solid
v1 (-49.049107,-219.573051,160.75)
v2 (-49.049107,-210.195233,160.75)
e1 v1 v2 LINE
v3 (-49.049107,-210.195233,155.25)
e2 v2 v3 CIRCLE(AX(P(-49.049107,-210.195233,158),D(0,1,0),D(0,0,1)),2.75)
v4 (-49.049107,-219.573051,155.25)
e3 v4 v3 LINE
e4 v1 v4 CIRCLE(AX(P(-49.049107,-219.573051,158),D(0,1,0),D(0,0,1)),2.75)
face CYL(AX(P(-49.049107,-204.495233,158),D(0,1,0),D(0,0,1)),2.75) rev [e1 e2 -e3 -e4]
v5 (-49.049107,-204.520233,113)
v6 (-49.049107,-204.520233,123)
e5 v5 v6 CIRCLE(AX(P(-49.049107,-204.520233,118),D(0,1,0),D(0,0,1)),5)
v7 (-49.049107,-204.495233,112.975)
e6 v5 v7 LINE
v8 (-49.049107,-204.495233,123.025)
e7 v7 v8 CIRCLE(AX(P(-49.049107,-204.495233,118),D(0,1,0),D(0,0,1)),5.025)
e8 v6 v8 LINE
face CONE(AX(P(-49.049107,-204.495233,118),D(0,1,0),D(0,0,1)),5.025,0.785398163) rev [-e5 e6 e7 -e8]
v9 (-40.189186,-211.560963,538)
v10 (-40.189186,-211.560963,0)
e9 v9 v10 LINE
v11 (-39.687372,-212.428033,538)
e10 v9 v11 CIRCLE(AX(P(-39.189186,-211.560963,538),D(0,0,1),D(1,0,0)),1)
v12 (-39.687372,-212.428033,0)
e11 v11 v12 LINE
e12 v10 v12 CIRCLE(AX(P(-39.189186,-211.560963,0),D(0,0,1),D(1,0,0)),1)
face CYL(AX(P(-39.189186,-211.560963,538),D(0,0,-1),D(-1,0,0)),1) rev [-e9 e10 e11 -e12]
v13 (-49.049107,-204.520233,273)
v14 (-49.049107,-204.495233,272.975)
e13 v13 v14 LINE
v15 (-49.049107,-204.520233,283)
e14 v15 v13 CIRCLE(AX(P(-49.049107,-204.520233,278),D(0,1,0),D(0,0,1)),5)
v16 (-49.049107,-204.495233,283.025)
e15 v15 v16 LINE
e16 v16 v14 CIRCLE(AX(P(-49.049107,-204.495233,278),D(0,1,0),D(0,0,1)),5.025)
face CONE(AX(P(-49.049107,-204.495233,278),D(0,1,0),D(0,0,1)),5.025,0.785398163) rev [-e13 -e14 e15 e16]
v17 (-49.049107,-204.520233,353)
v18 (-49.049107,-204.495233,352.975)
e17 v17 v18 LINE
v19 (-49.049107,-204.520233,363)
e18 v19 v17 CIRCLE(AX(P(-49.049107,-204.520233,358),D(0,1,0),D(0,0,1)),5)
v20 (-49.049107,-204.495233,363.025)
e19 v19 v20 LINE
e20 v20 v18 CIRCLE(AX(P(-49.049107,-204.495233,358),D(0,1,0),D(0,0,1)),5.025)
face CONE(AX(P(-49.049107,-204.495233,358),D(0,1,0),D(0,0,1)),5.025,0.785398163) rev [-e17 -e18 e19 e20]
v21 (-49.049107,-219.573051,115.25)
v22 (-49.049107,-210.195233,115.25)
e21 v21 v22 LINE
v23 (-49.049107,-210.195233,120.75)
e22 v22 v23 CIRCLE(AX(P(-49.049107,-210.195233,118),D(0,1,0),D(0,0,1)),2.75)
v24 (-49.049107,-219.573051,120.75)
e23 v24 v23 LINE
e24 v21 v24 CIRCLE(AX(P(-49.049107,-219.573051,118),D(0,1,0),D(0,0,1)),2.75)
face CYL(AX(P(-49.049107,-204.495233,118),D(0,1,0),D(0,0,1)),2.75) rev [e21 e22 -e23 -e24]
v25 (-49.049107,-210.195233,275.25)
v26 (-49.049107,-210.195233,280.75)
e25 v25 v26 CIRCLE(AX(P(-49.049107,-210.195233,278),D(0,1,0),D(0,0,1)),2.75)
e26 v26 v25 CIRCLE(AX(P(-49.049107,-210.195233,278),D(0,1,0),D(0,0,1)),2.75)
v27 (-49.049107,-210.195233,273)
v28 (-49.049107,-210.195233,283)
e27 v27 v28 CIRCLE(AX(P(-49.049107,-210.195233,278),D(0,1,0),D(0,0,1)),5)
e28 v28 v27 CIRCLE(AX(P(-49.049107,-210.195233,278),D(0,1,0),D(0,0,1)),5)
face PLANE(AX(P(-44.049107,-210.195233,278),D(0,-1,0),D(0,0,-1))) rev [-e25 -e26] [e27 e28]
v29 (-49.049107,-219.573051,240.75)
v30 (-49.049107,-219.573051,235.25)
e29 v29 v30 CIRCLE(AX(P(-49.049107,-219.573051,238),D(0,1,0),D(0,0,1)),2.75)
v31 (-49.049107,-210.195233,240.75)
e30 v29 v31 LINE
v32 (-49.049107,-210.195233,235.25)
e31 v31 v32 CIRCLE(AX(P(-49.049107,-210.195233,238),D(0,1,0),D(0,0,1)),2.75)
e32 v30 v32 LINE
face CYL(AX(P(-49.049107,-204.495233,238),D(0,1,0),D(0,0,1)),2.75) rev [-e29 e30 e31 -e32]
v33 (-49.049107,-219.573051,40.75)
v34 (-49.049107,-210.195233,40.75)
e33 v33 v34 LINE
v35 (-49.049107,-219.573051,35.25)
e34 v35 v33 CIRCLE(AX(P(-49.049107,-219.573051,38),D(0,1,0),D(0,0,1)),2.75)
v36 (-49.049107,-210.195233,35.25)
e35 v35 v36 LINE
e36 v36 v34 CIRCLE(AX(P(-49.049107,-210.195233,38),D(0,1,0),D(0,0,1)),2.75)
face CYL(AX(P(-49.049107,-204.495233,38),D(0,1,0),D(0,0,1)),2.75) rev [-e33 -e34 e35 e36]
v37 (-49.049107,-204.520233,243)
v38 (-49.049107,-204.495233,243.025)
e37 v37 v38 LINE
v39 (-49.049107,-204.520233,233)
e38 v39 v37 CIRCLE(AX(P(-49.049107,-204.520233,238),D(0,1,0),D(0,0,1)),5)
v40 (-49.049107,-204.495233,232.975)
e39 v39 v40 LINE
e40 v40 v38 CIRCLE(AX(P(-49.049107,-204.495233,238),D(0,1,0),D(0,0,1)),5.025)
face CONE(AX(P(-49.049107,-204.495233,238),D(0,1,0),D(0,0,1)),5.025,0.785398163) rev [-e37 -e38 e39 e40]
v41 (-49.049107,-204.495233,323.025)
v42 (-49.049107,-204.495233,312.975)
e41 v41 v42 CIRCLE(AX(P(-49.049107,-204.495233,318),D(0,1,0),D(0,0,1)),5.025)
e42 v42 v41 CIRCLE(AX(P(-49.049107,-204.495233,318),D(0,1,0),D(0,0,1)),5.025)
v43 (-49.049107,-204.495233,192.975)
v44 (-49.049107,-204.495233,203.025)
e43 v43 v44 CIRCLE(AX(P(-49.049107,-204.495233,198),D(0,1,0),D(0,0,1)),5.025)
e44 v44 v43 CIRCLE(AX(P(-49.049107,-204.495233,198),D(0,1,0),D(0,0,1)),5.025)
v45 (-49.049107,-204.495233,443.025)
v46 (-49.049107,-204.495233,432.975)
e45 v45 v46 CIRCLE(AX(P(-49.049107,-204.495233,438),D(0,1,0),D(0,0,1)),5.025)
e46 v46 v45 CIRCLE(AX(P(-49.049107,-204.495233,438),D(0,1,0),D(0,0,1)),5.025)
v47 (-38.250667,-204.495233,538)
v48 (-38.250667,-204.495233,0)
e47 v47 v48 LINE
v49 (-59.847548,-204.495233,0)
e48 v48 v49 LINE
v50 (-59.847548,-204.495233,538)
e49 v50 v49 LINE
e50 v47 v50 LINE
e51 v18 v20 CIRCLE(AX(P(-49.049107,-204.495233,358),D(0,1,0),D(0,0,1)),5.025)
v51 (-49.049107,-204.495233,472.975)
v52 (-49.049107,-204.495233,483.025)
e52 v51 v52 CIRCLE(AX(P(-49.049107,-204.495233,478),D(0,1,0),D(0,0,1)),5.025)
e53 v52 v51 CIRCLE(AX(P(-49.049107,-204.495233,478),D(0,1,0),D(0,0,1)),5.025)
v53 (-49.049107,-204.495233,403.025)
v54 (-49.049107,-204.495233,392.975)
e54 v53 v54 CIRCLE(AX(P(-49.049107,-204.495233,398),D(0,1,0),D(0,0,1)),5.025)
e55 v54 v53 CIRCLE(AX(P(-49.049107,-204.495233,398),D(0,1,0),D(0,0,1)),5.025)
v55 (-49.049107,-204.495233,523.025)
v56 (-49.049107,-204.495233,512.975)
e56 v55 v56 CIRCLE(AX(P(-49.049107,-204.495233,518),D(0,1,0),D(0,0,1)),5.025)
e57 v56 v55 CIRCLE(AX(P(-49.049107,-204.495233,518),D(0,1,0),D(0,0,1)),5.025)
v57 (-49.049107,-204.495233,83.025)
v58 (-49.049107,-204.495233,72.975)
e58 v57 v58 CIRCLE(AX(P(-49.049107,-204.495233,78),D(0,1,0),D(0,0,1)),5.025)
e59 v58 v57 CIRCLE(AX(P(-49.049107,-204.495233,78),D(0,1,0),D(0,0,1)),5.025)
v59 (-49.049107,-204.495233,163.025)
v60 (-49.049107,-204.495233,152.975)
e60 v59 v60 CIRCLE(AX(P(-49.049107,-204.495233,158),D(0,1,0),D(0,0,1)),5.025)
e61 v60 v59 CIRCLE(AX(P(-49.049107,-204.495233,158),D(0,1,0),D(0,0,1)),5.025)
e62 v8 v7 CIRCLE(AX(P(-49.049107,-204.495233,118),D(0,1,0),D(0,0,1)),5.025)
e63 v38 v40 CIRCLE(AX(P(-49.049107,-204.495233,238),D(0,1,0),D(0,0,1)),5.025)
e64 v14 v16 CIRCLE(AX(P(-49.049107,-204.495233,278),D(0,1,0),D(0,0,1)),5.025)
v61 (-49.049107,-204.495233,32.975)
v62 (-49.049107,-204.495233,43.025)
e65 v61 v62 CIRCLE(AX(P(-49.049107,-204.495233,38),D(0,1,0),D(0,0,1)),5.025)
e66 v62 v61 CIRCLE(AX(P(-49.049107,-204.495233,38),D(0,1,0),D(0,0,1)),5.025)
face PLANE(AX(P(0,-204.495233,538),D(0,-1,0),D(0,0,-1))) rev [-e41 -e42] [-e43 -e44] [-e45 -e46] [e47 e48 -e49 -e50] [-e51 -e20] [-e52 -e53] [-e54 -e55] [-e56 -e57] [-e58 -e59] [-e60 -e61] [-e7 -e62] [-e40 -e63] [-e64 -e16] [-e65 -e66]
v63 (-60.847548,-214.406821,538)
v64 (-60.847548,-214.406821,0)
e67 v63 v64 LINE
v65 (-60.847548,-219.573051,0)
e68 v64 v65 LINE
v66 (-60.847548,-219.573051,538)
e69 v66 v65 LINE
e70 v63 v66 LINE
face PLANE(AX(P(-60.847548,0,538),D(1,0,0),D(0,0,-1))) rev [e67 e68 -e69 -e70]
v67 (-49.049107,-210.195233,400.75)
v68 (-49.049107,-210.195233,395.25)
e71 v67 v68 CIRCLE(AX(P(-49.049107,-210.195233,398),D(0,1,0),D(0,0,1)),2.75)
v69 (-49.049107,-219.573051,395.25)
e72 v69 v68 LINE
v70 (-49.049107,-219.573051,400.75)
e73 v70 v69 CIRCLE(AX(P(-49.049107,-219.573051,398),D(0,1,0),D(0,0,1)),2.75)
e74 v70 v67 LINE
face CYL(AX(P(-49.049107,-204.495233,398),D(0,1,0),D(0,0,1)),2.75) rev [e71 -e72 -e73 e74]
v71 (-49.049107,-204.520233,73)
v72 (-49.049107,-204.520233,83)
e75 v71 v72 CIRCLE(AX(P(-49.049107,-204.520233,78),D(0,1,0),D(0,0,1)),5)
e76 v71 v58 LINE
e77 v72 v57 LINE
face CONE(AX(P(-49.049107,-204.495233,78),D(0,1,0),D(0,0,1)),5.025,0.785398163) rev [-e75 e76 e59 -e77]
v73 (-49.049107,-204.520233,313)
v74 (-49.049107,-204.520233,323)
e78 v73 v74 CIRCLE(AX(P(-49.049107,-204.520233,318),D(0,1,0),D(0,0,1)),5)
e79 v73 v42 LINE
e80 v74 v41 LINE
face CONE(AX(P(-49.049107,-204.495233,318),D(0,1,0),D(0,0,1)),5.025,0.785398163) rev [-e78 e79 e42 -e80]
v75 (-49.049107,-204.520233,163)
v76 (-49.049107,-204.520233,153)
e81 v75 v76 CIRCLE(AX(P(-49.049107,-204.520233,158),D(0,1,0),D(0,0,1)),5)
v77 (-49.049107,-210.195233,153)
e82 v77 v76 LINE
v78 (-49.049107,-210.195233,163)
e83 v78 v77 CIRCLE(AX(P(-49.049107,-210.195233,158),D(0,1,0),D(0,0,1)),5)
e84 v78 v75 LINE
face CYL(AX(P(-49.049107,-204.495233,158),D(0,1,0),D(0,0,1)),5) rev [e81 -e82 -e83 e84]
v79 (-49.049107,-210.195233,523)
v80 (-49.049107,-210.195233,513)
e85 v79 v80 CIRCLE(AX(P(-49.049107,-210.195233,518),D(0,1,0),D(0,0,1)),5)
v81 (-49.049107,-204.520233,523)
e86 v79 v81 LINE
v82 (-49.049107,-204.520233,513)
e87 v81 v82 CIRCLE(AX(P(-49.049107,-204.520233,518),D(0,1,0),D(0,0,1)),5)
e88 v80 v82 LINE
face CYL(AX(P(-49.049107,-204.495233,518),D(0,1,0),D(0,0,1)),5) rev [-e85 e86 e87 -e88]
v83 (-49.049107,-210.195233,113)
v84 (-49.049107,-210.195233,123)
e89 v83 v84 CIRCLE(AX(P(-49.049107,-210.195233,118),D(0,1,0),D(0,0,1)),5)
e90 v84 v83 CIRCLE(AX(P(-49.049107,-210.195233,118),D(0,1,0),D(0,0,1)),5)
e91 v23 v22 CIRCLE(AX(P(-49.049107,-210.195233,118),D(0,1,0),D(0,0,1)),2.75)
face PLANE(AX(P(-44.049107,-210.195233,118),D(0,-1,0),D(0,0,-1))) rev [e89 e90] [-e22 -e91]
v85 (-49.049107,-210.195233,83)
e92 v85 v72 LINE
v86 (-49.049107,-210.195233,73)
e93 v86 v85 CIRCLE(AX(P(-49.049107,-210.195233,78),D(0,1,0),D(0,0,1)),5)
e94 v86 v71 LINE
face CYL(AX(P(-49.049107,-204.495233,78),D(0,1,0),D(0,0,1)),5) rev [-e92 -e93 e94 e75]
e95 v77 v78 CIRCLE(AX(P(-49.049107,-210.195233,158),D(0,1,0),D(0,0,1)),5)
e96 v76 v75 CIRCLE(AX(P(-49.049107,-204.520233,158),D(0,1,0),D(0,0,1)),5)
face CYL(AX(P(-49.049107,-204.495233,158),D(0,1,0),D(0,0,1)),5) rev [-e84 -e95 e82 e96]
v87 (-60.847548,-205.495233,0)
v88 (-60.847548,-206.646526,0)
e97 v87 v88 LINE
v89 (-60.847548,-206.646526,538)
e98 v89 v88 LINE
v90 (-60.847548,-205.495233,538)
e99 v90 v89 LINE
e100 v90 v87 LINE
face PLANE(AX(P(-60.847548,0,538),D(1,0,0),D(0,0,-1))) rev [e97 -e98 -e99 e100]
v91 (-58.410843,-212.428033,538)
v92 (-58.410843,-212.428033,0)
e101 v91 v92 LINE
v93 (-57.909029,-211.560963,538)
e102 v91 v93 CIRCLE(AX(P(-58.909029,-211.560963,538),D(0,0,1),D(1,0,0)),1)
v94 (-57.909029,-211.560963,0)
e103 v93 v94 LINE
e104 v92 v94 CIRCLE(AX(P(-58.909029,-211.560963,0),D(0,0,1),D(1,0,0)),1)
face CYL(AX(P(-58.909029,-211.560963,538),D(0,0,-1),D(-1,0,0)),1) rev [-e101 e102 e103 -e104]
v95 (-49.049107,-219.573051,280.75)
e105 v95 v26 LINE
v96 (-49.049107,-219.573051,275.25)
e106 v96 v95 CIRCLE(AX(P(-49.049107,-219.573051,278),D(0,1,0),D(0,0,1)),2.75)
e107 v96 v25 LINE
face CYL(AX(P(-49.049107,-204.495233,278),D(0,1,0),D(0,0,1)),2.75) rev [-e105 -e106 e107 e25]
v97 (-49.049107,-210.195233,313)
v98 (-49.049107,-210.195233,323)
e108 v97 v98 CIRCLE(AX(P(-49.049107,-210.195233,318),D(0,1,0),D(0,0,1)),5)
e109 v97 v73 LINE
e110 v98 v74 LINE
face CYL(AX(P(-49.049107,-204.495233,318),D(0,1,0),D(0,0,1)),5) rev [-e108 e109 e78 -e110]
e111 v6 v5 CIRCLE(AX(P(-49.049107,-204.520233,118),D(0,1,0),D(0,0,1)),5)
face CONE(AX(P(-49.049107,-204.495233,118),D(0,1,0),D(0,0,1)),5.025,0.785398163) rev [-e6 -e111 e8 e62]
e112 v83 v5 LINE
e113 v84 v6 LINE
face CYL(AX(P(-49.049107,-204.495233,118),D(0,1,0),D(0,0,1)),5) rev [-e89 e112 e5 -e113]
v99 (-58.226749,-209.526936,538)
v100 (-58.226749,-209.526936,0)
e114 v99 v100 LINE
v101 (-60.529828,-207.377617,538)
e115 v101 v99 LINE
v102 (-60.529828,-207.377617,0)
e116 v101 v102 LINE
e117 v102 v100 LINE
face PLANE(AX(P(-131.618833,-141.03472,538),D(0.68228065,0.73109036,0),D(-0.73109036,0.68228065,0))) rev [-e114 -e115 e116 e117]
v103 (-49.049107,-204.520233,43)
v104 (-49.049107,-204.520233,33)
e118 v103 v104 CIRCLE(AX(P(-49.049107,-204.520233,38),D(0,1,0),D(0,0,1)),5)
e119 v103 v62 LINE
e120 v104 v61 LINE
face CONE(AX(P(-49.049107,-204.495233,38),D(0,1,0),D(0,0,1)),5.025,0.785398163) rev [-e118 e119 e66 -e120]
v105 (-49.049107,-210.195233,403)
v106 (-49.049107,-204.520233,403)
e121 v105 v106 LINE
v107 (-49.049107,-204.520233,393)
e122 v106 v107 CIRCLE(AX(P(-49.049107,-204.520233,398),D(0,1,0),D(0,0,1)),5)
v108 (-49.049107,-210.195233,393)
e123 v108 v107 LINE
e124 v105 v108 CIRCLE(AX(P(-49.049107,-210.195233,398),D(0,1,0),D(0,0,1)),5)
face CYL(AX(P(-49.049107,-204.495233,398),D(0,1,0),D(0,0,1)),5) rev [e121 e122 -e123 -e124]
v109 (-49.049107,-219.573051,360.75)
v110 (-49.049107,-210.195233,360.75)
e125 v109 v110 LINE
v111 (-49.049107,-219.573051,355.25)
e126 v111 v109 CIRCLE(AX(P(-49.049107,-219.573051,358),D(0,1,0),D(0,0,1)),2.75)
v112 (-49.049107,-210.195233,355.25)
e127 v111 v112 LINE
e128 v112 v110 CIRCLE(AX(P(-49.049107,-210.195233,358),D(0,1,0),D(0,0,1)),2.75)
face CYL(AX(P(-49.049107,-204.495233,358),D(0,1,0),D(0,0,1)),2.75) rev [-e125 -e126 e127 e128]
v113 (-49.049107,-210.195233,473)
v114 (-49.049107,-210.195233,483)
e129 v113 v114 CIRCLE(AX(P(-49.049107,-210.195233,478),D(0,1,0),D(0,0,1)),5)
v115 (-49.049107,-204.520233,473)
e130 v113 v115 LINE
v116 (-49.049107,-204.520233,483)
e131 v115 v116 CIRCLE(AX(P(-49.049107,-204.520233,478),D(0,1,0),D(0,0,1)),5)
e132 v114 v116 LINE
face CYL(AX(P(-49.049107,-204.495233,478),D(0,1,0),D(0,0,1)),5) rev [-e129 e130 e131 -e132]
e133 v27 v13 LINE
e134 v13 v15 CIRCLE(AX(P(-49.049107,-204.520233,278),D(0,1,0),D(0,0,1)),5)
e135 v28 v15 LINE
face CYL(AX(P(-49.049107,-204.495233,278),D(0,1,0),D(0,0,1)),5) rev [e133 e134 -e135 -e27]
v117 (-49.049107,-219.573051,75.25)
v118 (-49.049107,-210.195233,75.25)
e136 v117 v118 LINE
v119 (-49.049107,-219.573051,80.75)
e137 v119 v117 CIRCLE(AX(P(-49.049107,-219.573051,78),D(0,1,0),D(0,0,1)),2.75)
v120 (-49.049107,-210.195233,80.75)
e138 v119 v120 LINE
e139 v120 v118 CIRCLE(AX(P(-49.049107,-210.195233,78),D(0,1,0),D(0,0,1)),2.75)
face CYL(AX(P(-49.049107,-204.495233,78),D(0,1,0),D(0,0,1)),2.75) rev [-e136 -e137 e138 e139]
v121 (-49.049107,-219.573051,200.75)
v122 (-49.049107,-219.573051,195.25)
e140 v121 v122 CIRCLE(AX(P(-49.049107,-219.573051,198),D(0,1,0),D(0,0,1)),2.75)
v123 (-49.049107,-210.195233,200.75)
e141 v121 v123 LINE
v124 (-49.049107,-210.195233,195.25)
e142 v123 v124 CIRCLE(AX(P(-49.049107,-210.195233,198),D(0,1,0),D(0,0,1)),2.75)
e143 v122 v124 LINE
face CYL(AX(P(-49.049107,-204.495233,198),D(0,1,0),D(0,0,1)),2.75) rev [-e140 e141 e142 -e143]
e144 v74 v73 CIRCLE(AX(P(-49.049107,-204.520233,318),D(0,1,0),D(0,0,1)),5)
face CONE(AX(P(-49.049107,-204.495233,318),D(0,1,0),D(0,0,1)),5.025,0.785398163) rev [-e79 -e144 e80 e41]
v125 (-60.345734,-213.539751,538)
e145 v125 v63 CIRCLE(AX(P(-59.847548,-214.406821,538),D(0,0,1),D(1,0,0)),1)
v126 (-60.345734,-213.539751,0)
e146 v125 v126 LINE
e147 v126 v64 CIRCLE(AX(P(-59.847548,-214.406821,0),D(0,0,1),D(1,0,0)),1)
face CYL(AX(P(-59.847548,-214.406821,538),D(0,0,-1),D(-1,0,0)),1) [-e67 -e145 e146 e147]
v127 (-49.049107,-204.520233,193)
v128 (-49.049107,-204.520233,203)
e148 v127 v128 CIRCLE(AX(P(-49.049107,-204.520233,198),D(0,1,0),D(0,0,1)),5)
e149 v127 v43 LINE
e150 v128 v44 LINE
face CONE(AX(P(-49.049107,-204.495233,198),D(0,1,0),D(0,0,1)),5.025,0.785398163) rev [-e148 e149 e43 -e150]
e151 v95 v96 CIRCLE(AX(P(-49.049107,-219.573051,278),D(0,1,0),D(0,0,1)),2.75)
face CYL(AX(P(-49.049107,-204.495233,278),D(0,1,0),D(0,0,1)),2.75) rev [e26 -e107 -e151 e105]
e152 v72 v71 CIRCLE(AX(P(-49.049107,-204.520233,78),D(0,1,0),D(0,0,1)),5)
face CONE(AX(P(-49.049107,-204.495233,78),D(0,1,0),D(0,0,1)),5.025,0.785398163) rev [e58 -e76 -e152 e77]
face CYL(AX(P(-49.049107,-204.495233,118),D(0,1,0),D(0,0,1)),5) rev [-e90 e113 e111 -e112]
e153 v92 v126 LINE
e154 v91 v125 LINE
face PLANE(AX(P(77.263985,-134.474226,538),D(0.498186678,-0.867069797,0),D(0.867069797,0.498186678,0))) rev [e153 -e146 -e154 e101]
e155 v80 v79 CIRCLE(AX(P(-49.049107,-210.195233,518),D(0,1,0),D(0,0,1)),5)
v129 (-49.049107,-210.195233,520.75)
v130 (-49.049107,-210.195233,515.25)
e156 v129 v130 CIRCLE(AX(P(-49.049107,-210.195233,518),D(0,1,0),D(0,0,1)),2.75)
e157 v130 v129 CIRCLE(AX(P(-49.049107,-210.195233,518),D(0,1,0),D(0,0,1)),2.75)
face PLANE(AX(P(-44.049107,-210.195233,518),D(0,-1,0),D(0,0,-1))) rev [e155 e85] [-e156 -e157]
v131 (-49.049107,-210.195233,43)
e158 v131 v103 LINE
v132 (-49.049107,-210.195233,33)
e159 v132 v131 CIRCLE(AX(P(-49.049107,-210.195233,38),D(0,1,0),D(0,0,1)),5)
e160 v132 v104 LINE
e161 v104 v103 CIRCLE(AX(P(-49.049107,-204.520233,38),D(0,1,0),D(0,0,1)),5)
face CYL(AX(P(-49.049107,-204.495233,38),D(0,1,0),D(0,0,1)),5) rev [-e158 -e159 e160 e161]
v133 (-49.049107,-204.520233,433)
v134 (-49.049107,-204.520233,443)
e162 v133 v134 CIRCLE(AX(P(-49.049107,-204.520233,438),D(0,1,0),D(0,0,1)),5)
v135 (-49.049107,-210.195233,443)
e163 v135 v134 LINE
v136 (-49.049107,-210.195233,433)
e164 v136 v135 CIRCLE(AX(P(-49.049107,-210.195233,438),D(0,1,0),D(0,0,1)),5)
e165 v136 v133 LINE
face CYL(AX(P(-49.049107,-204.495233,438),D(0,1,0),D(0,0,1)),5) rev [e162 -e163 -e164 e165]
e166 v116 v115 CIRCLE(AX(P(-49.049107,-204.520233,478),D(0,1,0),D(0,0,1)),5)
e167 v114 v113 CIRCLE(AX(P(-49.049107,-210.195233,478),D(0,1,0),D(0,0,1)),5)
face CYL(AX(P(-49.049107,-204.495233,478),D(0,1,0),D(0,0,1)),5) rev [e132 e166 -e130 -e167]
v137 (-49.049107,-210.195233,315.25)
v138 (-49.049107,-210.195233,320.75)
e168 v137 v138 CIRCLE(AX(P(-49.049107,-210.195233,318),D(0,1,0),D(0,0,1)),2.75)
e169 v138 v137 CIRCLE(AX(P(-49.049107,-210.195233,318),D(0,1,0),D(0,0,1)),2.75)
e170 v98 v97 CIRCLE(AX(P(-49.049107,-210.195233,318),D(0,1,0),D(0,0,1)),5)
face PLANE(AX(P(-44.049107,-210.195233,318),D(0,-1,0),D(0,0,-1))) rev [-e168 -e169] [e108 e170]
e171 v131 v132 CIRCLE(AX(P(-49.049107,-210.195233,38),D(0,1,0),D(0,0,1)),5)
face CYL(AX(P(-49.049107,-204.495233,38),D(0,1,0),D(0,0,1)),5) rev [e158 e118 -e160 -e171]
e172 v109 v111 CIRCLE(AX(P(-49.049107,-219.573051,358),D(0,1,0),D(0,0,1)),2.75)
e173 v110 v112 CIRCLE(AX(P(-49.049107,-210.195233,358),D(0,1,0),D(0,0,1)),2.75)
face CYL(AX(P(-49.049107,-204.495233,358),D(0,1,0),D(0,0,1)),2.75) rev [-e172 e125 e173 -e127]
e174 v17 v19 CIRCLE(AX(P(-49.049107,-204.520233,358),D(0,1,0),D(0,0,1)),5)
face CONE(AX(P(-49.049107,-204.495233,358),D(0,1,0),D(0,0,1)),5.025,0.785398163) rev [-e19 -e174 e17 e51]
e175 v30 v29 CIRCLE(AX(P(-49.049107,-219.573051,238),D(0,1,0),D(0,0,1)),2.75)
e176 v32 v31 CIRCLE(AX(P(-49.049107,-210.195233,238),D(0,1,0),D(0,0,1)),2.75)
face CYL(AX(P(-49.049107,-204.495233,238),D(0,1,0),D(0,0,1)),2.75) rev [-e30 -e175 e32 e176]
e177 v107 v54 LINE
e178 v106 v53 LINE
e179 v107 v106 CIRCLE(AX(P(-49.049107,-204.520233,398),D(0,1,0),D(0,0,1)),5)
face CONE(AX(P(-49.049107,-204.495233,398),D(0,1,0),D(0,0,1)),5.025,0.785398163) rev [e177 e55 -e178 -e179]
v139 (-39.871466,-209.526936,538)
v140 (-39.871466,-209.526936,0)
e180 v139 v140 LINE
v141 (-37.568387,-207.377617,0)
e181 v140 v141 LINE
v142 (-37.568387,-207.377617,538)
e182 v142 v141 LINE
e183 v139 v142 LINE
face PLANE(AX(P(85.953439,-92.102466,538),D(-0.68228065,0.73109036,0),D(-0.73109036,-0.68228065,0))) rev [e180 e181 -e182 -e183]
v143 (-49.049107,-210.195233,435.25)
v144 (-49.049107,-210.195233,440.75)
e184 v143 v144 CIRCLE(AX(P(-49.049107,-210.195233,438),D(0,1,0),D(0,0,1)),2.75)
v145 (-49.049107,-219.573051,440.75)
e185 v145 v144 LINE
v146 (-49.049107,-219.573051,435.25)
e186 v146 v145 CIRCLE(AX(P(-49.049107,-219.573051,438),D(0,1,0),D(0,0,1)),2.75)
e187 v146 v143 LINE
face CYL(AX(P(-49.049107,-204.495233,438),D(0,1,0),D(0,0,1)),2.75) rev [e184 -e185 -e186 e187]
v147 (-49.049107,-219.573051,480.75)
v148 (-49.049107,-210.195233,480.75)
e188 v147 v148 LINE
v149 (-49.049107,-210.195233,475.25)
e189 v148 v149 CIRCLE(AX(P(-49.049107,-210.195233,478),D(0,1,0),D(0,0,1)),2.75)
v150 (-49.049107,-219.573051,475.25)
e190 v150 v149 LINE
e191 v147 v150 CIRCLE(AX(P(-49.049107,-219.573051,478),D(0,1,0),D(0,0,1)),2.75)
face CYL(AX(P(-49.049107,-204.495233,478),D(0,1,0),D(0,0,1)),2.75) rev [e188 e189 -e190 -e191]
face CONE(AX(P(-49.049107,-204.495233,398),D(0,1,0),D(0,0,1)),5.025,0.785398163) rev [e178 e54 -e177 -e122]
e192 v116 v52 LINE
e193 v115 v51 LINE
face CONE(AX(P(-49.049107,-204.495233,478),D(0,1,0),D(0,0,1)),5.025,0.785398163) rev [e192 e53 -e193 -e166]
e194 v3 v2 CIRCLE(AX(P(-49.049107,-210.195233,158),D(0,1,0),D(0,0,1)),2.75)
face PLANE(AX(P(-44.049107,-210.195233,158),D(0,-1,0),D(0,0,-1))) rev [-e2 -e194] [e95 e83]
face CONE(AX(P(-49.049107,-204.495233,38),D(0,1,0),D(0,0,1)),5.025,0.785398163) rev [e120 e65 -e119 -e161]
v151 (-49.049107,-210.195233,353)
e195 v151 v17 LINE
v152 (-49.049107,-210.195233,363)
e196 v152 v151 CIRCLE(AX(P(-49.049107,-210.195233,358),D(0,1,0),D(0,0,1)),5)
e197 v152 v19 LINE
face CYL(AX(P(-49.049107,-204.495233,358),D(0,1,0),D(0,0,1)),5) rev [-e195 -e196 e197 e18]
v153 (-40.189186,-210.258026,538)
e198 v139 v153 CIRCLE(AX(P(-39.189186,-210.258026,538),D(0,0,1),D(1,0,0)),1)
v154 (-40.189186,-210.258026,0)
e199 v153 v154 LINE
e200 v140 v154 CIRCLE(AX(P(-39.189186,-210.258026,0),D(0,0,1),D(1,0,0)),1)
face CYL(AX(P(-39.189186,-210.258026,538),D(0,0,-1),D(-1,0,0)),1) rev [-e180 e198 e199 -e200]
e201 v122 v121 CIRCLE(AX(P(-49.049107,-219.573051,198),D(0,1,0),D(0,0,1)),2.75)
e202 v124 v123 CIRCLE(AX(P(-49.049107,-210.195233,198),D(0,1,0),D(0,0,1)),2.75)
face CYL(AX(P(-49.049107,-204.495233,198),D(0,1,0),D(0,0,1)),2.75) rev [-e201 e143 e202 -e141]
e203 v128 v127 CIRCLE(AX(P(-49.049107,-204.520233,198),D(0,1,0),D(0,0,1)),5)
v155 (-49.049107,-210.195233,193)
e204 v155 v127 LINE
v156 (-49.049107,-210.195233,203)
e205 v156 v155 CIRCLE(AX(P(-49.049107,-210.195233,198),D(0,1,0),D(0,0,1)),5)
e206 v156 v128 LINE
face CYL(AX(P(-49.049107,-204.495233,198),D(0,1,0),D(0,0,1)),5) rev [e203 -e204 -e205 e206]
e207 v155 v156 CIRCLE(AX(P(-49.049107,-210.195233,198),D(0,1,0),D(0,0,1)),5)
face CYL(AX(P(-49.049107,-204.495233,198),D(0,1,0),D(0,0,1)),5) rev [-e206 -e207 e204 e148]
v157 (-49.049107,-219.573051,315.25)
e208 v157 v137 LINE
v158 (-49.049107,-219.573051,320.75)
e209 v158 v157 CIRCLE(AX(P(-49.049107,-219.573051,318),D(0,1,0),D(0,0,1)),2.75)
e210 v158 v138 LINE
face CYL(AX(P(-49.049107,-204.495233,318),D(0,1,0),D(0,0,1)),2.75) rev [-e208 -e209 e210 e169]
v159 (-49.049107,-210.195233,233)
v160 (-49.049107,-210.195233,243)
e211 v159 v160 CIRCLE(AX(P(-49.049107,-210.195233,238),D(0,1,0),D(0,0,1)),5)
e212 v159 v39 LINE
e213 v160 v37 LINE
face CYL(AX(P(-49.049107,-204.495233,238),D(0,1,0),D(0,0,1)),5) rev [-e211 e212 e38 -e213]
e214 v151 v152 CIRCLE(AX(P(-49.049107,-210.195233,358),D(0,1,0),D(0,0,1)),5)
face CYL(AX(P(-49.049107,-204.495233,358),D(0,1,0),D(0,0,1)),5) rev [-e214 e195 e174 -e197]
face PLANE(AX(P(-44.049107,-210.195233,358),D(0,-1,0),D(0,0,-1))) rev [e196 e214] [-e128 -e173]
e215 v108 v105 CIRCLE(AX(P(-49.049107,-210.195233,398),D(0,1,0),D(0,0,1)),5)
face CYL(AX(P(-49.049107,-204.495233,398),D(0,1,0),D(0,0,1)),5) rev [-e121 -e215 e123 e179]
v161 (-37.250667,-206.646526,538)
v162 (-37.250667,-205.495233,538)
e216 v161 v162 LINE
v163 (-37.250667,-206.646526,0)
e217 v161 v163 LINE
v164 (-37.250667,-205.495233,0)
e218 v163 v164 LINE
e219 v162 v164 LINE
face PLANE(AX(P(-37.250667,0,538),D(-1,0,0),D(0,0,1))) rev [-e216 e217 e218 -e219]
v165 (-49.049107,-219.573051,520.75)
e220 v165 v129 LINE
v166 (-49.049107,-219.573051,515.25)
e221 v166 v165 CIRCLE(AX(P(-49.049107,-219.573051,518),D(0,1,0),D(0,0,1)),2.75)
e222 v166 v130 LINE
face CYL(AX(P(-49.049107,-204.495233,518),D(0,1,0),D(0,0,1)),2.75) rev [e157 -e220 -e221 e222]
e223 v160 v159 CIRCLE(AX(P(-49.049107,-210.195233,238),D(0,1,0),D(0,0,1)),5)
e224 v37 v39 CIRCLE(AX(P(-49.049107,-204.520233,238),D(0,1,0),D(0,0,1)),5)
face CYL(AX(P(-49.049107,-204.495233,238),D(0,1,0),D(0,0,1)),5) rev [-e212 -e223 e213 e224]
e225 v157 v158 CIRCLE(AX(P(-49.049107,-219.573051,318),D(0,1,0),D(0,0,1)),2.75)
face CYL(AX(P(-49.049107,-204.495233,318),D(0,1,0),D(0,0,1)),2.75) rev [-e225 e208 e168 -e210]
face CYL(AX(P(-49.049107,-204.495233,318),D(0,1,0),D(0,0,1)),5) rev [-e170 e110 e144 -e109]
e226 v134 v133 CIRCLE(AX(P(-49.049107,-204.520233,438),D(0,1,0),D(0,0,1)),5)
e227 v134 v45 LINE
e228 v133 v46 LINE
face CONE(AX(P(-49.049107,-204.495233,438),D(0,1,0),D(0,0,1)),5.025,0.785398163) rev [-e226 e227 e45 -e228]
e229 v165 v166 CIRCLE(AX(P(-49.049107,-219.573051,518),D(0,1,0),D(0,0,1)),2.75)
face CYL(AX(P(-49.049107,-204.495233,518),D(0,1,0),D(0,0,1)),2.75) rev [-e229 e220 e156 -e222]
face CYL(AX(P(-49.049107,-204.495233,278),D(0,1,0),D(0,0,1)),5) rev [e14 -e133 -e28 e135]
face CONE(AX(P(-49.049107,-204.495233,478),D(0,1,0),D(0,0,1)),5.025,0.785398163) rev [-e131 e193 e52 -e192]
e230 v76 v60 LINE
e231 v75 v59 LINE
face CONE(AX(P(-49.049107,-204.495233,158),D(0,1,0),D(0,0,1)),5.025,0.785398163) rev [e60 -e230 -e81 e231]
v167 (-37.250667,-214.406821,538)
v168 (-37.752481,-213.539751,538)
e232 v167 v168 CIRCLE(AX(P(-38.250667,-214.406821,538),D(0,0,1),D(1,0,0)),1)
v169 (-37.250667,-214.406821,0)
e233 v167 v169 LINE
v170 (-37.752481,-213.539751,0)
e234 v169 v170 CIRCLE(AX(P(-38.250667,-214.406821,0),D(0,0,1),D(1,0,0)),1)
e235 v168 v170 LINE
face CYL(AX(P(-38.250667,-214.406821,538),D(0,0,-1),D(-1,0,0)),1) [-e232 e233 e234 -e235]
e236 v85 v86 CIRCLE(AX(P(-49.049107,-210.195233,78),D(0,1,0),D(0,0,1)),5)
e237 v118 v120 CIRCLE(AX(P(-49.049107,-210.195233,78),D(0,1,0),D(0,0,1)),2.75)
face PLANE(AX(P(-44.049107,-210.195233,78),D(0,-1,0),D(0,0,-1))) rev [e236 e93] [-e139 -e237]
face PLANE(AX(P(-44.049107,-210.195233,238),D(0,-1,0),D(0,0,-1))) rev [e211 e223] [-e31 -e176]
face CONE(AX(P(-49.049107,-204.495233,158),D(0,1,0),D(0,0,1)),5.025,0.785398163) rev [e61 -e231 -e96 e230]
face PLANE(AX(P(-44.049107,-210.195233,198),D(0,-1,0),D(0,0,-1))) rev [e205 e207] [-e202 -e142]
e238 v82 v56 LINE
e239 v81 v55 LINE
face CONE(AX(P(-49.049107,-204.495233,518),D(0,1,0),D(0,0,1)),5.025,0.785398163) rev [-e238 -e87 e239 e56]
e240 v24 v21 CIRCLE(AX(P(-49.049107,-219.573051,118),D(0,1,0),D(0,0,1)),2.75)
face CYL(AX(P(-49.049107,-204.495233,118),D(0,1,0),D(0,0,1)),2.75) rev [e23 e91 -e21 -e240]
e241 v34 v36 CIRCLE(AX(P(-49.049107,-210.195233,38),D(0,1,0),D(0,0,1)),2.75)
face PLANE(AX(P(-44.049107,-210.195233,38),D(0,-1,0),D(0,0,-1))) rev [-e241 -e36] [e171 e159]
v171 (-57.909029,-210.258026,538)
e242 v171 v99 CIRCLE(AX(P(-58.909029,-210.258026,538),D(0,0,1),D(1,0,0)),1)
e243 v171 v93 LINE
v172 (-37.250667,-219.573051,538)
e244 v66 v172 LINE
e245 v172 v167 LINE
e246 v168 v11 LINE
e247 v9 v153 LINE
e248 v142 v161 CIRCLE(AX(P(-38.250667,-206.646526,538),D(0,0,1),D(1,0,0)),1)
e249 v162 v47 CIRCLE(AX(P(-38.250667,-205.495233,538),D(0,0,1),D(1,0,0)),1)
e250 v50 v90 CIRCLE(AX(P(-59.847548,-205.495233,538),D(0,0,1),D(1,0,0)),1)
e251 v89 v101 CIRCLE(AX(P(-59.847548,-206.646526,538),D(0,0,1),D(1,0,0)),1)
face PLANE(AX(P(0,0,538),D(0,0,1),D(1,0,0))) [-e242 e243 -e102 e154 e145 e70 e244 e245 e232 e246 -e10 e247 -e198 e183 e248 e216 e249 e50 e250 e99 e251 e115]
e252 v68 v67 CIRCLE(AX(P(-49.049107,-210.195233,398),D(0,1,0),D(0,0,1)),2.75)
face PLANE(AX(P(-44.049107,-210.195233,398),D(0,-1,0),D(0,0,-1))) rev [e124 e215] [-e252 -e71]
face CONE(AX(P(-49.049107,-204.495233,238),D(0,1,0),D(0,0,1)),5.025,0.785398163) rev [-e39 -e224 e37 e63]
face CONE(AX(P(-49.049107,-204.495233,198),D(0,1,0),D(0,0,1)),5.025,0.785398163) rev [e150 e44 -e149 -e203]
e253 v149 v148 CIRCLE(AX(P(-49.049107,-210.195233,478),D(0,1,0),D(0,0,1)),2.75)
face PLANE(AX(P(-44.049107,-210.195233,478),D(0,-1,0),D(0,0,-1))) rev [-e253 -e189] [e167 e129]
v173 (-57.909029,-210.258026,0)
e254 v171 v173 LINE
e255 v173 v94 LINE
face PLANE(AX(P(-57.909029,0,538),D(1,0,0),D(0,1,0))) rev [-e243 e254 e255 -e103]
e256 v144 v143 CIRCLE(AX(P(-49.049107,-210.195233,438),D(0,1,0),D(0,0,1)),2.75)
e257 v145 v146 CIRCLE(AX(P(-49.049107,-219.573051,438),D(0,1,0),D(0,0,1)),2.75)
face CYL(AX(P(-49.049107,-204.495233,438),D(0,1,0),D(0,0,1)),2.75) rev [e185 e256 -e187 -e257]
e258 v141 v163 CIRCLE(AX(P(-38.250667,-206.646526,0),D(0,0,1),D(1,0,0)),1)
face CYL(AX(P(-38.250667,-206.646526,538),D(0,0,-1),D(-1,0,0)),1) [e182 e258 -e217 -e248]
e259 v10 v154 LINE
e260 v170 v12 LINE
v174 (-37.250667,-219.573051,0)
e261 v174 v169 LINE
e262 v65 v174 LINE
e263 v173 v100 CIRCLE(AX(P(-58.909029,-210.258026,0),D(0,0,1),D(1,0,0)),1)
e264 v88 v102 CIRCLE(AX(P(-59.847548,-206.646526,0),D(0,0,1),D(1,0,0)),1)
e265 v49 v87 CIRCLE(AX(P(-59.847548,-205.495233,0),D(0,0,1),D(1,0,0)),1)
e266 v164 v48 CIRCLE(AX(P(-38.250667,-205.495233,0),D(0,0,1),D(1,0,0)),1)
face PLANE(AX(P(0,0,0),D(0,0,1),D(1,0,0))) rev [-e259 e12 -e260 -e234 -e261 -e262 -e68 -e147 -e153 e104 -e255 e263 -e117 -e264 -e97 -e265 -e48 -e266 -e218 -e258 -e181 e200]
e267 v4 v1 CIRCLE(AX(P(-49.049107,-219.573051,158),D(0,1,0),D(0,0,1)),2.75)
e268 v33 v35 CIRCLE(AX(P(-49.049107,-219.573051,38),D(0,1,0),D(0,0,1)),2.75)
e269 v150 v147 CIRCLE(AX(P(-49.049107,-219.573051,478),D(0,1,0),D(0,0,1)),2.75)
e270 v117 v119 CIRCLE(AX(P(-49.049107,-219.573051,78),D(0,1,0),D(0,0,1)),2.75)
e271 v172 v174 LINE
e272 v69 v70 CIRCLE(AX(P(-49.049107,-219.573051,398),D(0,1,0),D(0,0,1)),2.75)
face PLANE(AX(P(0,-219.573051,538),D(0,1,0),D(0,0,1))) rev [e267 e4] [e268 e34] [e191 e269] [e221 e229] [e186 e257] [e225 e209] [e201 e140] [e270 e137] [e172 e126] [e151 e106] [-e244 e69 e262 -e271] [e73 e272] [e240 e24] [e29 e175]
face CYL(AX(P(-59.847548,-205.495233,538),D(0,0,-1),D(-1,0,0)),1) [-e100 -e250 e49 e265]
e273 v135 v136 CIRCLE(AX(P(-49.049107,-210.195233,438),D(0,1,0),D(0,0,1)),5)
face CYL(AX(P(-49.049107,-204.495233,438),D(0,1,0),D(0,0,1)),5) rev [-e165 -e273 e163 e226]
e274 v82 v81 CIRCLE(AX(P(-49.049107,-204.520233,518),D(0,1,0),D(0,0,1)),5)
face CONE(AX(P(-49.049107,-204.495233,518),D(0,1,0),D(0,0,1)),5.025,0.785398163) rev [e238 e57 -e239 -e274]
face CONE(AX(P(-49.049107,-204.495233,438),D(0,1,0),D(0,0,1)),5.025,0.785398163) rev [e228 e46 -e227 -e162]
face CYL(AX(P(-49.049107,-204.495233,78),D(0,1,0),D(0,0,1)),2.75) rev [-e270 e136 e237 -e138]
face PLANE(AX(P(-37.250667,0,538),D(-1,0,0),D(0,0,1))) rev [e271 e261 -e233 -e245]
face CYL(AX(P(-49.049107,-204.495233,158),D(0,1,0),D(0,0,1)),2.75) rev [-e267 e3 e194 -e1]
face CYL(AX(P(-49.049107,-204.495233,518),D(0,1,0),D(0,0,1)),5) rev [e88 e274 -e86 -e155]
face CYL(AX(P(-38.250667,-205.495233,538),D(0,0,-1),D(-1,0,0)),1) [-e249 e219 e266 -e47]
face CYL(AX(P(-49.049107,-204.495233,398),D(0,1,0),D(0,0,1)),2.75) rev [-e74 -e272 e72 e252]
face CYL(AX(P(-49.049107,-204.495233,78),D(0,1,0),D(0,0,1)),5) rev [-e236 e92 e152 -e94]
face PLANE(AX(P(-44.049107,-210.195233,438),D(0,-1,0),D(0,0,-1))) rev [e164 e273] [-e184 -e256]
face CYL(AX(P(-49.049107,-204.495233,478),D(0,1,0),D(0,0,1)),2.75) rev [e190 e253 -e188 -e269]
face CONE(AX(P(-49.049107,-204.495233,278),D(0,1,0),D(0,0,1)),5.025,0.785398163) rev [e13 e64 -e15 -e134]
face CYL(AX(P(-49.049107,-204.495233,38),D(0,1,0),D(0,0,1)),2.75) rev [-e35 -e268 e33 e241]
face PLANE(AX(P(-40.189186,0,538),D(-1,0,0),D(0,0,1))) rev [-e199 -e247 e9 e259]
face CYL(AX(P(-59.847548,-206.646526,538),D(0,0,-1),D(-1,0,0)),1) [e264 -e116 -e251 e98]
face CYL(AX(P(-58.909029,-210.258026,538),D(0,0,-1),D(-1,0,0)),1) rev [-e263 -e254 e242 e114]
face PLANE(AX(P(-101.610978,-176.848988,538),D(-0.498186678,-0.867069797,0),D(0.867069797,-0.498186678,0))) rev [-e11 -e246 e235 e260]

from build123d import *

# Parameters (mm, degrees)
BOSS_EXTRUDE1_DEPTH                           = 538
CBORE_FOR_M5_HEXAGON_SOCKET_HEAD_CAP_2_COUNT  = 2
CBORE_FOR_M5_HEXAGON_SOCKET_HEAD_CAP_2_PITCH  = 40
CBORE_FOR_M5_HEXAGON_SOCKET_HEAD_CAP_3_COUNT  = 2
CBORE_FOR_M5_HEXAGON_SOCKET_HEAD_CAP_3_PITCH  = 80
CBORE_FOR_M5_HEXAGON_SOCKET_HEAD_CAP_4_COUNT  = 2
CBORE_FOR_M5_HEXAGON_SOCKET_HEAD_CAP_4_PITCH  = 120
CBORE_FOR_M5_HEXAGON_SOCKET_HEAD_CAP_5_COUNT  = 2
CBORE_FOR_M5_HEXAGON_SOCKET_HEAD_CAP_5_PITCH  = 160
CBORE_FOR_M5_HEXAGON_SOCKET_HEAD_CAP_6_COUNT  = 2
CBORE_FOR_M5_HEXAGON_SOCKET_HEAD_CAP_6_PITCH  = 200
CBORE_FOR_M5_HEXAGON_SOCKET_HEAD_CAP_7_COUNT  = 2
CBORE_FOR_M5_HEXAGON_SOCKET_HEAD_CAP_7_PITCH  = 240
CBORE_FOR_M5_HEXAGON_SOCKET_HEAD_CAP_8_COUNT  = 2
CBORE_FOR_M5_HEXAGON_SOCKET_HEAD_CAP_8_PITCH  = 280
CBORE_FOR_M5_HEXAGON_SOCKET_HEAD_CAP_9_COUNT  = 2
CBORE_FOR_M5_HEXAGON_SOCKET_HEAD_CAP_9_PITCH  = 320
CBORE_FOR_M5_HEXAGON_SOCKET_HEAD_CAP_10_COUNT = 2
CBORE_FOR_M5_HEXAGON_SOCKET_HEAD_CAP_10_PITCH = 360
CBORE_FOR_M5_HEXAGON_SOCKET_HEAD_CAP_11_COUNT = 2
CBORE_FOR_M5_HEXAGON_SOCKET_HEAD_CAP_11_PITCH = 400
CBORE_FOR_M5_HEXAGON_SOCKET_HEAD_CAP_12_COUNT = 2
CBORE_FOR_M5_HEXAGON_SOCKET_HEAD_CAP_12_PITCH = 440
CBORE_FOR_M5_HEXAGON_SOCKET_HEAD_CAP_13_COUNT = 2
CBORE_FOR_M5_HEXAGON_SOCKET_HEAD_CAP_13_PITCH = 480


with BuildPart() as part:
    # Sketch1 → Boss-Extrude1 (new body)
    with BuildSketch(Plane.XY):
        with BuildLine():
            Line((-49.04910749, -219.573051322), (-49.04910749, -215.151654368))
            Line((-49.04910749, -215.151654368), (-49.04910749, -204.495232783))
            Line((-49.04910749, -204.495232783), (-59.847547756, -204.495232783))
            ThreePointArc((-59.847547756, -204.495232783), (-60.554654537, -204.788126002), (-60.847547756, -205.495232783))
            Line((-60.847547756, -205.495232783), (-60.847547756, -206.646526247))
            ThreePointArc((-60.847547756, -206.646526247), (-60.764684782, -207.045098292), (-60.529828406, -207.377616608))
            Line((-60.529828406, -207.377616608), (-58.226748647, -209.52693609))
            ThreePointArc((-58.226748647, -209.52693609), (-57.991892271, -209.859454405), (-57.909029297, -210.25802645))
            Line((-57.909029297, -210.25802645), (-57.909029297, -211.560962818))
            ThreePointArc((-57.909029297, -211.560962818), (-58.043527512, -212.061868659), (-58.410842619, -212.428032616))
            Line((-58.410842619, -212.428032616), (-60.345734434, -213.539750876))
            ThreePointArc((-60.345734434, -213.539750876), (-60.713049541, -213.905914833), (-60.847547756, -214.406820673))
            Line((-60.847547756, -214.406820673), (-60.847547756, -219.573051322))
            Line((-60.847547756, -219.573051322), (-49.04910749, -219.573051322))
        make_face()
        with BuildLine():
            Line((-49.04910749, -204.495232783), (-49.04910749, -215.151654368))
            Line((-49.04910749, -215.151654368), (-49.04910749, -219.573051322))
            Line((-49.04910749, -219.573051322), (-37.250667225, -219.573051322))
            Line((-37.250667225, -219.573051322), (-37.250667225, -214.406820673))
            ThreePointArc((-37.250667225, -214.406820673), (-37.38516544, -213.905914833), (-37.752480546, -213.539750876))
            Line((-37.752480546, -213.539750876), (-39.687372362, -212.428032616))
            ThreePointArc((-39.687372362, -212.428032616), (-40.054687468, -212.061868659), (-40.189185684, -211.560962818))
            Line((-40.189185684, -211.560962818), (-40.189185684, -210.25802645))
            ThreePointArc((-40.189185684, -210.25802645), (-40.10632271, -209.859454405), (-39.871466333, -209.52693609))
            Line((-39.871466333, -209.52693609), (-37.568386575, -207.377616608))
            ThreePointArc((-37.568386575, -207.377616608), (-37.333530198, -207.045098292), (-37.250667225, -206.646526247))
            Line((-37.250667225, -206.646526247), (-37.250667225, -205.495232783))
            ThreePointArc((-37.250667225, -205.495232783), (-37.543560443, -204.788126002), (-38.250667225, -204.495232783))
            Line((-38.250667225, -204.495232783), (-49.04910749, -204.495232783))
        make_face()
    extrude(amount=BOSS_EXTRUDE1_DEPTH)

    # Sketch3 → CBORE for M5 Hexagon socket head cap screws1 (revolve, cut)
    with BuildSketch(Plane(origin=(-49.04910749, -204.495232783, 518), x_dir=(0, 0, 1), z_dir=(1, 0, 0))):
        Polygon((0, 0), (0, 15.077818539), (2.75, 15.077818539), (2.75, 5.7), (5, 5.7), (5, 0.025), (5.025, 0), align=None)
    cbore_for_m5_hexagon_socket_head_cap_scr = revolve(axis=Axis((-49.04910749, -198.145232783, 518), (0, -1, 0)), mode=Mode.SUBTRACT)

    # CBORE for M5 Hexagon socket head cap 2: CBORE for M5 Hexagon socket head cap screws1 ×2
    with Locations(*[(0, 0, -i * CBORE_FOR_M5_HEXAGON_SOCKET_HEAD_CAP_2_PITCH) for i in range(1, CBORE_FOR_M5_HEXAGON_SOCKET_HEAD_CAP_2_COUNT)]):
        add(cbore_for_m5_hexagon_socket_head_cap_scr, mode=Mode.SUBTRACT)

    # CBORE for M5 Hexagon socket head cap 3: CBORE for M5 Hexagon socket head cap screws1 ×2
    with Locations(*[(0, 0, -i * CBORE_FOR_M5_HEXAGON_SOCKET_HEAD_CAP_3_PITCH) for i in range(1, CBORE_FOR_M5_HEXAGON_SOCKET_HEAD_CAP_3_COUNT)]):
        add(cbore_for_m5_hexagon_socket_head_cap_scr, mode=Mode.SUBTRACT)

    # CBORE for M5 Hexagon socket head cap 4: CBORE for M5 Hexagon socket head cap screws1 ×2
    with Locations(*[(0, 0, -i * CBORE_FOR_M5_HEXAGON_SOCKET_HEAD_CAP_4_PITCH) for i in range(1, CBORE_FOR_M5_HEXAGON_SOCKET_HEAD_CAP_4_COUNT)]):
        add(cbore_for_m5_hexagon_socket_head_cap_scr, mode=Mode.SUBTRACT)

    # CBORE for M5 Hexagon socket head cap 5: CBORE for M5 Hexagon socket head cap screws1 ×2
    with Locations(*[(0, 0, -i * CBORE_FOR_M5_HEXAGON_SOCKET_HEAD_CAP_5_PITCH) for i in range(1, CBORE_FOR_M5_HEXAGON_SOCKET_HEAD_CAP_5_COUNT)]):
        add(cbore_for_m5_hexagon_socket_head_cap_scr, mode=Mode.SUBTRACT)

    # CBORE for M5 Hexagon socket head cap 6: CBORE for M5 Hexagon socket head cap screws1 ×2
    with Locations(*[(0, 0, -i * CBORE_FOR_M5_HEXAGON_SOCKET_HEAD_CAP_6_PITCH) for i in range(1, CBORE_FOR_M5_HEXAGON_SOCKET_HEAD_CAP_6_COUNT)]):
        add(cbore_for_m5_hexagon_socket_head_cap_scr, mode=Mode.SUBTRACT)

    # CBORE for M5 Hexagon socket head cap 7: CBORE for M5 Hexagon socket head cap screws1 ×2
    with Locations(*[(0, 0, -i * CBORE_FOR_M5_HEXAGON_SOCKET_HEAD_CAP_7_PITCH) for i in range(1, CBORE_FOR_M5_HEXAGON_SOCKET_HEAD_CAP_7_COUNT)]):
        add(cbore_for_m5_hexagon_socket_head_cap_scr, mode=Mode.SUBTRACT)

    # CBORE for M5 Hexagon socket head cap 8: CBORE for M5 Hexagon socket head cap screws1 ×2
    with Locations(*[(0, 0, -i * CBORE_FOR_M5_HEXAGON_SOCKET_HEAD_CAP_8_PITCH) for i in range(1, CBORE_FOR_M5_HEXAGON_SOCKET_HEAD_CAP_8_COUNT)]):
        add(cbore_for_m5_hexagon_socket_head_cap_scr, mode=Mode.SUBTRACT)

    # CBORE for M5 Hexagon socket head cap 9: CBORE for M5 Hexagon socket head cap screws1 ×2
    with Locations(*[(0, 0, -i * CBORE_FOR_M5_HEXAGON_SOCKET_HEAD_CAP_9_PITCH) for i in range(1, CBORE_FOR_M5_HEXAGON_SOCKET_HEAD_CAP_9_COUNT)]):
        add(cbore_for_m5_hexagon_socket_head_cap_scr, mode=Mode.SUBTRACT)

    # CBORE for M5 Hexagon socket head cap 10: CBORE for M5 Hexagon socket head cap screws1 ×2
    with Locations(*[(0, 0, -i * CBORE_FOR_M5_HEXAGON_SOCKET_HEAD_CAP_10_PITCH) for i in range(1, CBORE_FOR_M5_HEXAGON_SOCKET_HEAD_CAP_10_COUNT)]):
        add(cbore_for_m5_hexagon_socket_head_cap_scr, mode=Mode.SUBTRACT)

    # CBORE for M5 Hexagon socket head cap 11: CBORE for M5 Hexagon socket head cap screws1 ×2
    with Locations(*[(0, 0, -i * CBORE_FOR_M5_HEXAGON_SOCKET_HEAD_CAP_11_PITCH) for i in range(1, CBORE_FOR_M5_HEXAGON_SOCKET_HEAD_CAP_11_COUNT)]):
        add(cbore_for_m5_hexagon_socket_head_cap_scr, mode=Mode.SUBTRACT)

    # CBORE for M5 Hexagon socket head cap 12: CBORE for M5 Hexagon socket head cap screws1 ×2
    with Locations(*[(0, 0, -i * CBORE_FOR_M5_HEXAGON_SOCKET_HEAD_CAP_12_PITCH) for i in range(1, CBORE_FOR_M5_HEXAGON_SOCKET_HEAD_CAP_12_COUNT)]):
        add(cbore_for_m5_hexagon_socket_head_cap_scr, mode=Mode.SUBTRACT)

    # CBORE for M5 Hexagon socket head cap 13: CBORE for M5 Hexagon socket head cap screws1 ×2
    with Locations(*[(0, 0, -i * CBORE_FOR_M5_HEXAGON_SOCKET_HEAD_CAP_13_PITCH) for i in range(1, CBORE_FOR_M5_HEXAGON_SOCKET_HEAD_CAP_13_COUNT)]):
        add(cbore_for_m5_hexagon_socket_head_cap_scr, mode=Mode.SUBTRACT)


solid = part.part
